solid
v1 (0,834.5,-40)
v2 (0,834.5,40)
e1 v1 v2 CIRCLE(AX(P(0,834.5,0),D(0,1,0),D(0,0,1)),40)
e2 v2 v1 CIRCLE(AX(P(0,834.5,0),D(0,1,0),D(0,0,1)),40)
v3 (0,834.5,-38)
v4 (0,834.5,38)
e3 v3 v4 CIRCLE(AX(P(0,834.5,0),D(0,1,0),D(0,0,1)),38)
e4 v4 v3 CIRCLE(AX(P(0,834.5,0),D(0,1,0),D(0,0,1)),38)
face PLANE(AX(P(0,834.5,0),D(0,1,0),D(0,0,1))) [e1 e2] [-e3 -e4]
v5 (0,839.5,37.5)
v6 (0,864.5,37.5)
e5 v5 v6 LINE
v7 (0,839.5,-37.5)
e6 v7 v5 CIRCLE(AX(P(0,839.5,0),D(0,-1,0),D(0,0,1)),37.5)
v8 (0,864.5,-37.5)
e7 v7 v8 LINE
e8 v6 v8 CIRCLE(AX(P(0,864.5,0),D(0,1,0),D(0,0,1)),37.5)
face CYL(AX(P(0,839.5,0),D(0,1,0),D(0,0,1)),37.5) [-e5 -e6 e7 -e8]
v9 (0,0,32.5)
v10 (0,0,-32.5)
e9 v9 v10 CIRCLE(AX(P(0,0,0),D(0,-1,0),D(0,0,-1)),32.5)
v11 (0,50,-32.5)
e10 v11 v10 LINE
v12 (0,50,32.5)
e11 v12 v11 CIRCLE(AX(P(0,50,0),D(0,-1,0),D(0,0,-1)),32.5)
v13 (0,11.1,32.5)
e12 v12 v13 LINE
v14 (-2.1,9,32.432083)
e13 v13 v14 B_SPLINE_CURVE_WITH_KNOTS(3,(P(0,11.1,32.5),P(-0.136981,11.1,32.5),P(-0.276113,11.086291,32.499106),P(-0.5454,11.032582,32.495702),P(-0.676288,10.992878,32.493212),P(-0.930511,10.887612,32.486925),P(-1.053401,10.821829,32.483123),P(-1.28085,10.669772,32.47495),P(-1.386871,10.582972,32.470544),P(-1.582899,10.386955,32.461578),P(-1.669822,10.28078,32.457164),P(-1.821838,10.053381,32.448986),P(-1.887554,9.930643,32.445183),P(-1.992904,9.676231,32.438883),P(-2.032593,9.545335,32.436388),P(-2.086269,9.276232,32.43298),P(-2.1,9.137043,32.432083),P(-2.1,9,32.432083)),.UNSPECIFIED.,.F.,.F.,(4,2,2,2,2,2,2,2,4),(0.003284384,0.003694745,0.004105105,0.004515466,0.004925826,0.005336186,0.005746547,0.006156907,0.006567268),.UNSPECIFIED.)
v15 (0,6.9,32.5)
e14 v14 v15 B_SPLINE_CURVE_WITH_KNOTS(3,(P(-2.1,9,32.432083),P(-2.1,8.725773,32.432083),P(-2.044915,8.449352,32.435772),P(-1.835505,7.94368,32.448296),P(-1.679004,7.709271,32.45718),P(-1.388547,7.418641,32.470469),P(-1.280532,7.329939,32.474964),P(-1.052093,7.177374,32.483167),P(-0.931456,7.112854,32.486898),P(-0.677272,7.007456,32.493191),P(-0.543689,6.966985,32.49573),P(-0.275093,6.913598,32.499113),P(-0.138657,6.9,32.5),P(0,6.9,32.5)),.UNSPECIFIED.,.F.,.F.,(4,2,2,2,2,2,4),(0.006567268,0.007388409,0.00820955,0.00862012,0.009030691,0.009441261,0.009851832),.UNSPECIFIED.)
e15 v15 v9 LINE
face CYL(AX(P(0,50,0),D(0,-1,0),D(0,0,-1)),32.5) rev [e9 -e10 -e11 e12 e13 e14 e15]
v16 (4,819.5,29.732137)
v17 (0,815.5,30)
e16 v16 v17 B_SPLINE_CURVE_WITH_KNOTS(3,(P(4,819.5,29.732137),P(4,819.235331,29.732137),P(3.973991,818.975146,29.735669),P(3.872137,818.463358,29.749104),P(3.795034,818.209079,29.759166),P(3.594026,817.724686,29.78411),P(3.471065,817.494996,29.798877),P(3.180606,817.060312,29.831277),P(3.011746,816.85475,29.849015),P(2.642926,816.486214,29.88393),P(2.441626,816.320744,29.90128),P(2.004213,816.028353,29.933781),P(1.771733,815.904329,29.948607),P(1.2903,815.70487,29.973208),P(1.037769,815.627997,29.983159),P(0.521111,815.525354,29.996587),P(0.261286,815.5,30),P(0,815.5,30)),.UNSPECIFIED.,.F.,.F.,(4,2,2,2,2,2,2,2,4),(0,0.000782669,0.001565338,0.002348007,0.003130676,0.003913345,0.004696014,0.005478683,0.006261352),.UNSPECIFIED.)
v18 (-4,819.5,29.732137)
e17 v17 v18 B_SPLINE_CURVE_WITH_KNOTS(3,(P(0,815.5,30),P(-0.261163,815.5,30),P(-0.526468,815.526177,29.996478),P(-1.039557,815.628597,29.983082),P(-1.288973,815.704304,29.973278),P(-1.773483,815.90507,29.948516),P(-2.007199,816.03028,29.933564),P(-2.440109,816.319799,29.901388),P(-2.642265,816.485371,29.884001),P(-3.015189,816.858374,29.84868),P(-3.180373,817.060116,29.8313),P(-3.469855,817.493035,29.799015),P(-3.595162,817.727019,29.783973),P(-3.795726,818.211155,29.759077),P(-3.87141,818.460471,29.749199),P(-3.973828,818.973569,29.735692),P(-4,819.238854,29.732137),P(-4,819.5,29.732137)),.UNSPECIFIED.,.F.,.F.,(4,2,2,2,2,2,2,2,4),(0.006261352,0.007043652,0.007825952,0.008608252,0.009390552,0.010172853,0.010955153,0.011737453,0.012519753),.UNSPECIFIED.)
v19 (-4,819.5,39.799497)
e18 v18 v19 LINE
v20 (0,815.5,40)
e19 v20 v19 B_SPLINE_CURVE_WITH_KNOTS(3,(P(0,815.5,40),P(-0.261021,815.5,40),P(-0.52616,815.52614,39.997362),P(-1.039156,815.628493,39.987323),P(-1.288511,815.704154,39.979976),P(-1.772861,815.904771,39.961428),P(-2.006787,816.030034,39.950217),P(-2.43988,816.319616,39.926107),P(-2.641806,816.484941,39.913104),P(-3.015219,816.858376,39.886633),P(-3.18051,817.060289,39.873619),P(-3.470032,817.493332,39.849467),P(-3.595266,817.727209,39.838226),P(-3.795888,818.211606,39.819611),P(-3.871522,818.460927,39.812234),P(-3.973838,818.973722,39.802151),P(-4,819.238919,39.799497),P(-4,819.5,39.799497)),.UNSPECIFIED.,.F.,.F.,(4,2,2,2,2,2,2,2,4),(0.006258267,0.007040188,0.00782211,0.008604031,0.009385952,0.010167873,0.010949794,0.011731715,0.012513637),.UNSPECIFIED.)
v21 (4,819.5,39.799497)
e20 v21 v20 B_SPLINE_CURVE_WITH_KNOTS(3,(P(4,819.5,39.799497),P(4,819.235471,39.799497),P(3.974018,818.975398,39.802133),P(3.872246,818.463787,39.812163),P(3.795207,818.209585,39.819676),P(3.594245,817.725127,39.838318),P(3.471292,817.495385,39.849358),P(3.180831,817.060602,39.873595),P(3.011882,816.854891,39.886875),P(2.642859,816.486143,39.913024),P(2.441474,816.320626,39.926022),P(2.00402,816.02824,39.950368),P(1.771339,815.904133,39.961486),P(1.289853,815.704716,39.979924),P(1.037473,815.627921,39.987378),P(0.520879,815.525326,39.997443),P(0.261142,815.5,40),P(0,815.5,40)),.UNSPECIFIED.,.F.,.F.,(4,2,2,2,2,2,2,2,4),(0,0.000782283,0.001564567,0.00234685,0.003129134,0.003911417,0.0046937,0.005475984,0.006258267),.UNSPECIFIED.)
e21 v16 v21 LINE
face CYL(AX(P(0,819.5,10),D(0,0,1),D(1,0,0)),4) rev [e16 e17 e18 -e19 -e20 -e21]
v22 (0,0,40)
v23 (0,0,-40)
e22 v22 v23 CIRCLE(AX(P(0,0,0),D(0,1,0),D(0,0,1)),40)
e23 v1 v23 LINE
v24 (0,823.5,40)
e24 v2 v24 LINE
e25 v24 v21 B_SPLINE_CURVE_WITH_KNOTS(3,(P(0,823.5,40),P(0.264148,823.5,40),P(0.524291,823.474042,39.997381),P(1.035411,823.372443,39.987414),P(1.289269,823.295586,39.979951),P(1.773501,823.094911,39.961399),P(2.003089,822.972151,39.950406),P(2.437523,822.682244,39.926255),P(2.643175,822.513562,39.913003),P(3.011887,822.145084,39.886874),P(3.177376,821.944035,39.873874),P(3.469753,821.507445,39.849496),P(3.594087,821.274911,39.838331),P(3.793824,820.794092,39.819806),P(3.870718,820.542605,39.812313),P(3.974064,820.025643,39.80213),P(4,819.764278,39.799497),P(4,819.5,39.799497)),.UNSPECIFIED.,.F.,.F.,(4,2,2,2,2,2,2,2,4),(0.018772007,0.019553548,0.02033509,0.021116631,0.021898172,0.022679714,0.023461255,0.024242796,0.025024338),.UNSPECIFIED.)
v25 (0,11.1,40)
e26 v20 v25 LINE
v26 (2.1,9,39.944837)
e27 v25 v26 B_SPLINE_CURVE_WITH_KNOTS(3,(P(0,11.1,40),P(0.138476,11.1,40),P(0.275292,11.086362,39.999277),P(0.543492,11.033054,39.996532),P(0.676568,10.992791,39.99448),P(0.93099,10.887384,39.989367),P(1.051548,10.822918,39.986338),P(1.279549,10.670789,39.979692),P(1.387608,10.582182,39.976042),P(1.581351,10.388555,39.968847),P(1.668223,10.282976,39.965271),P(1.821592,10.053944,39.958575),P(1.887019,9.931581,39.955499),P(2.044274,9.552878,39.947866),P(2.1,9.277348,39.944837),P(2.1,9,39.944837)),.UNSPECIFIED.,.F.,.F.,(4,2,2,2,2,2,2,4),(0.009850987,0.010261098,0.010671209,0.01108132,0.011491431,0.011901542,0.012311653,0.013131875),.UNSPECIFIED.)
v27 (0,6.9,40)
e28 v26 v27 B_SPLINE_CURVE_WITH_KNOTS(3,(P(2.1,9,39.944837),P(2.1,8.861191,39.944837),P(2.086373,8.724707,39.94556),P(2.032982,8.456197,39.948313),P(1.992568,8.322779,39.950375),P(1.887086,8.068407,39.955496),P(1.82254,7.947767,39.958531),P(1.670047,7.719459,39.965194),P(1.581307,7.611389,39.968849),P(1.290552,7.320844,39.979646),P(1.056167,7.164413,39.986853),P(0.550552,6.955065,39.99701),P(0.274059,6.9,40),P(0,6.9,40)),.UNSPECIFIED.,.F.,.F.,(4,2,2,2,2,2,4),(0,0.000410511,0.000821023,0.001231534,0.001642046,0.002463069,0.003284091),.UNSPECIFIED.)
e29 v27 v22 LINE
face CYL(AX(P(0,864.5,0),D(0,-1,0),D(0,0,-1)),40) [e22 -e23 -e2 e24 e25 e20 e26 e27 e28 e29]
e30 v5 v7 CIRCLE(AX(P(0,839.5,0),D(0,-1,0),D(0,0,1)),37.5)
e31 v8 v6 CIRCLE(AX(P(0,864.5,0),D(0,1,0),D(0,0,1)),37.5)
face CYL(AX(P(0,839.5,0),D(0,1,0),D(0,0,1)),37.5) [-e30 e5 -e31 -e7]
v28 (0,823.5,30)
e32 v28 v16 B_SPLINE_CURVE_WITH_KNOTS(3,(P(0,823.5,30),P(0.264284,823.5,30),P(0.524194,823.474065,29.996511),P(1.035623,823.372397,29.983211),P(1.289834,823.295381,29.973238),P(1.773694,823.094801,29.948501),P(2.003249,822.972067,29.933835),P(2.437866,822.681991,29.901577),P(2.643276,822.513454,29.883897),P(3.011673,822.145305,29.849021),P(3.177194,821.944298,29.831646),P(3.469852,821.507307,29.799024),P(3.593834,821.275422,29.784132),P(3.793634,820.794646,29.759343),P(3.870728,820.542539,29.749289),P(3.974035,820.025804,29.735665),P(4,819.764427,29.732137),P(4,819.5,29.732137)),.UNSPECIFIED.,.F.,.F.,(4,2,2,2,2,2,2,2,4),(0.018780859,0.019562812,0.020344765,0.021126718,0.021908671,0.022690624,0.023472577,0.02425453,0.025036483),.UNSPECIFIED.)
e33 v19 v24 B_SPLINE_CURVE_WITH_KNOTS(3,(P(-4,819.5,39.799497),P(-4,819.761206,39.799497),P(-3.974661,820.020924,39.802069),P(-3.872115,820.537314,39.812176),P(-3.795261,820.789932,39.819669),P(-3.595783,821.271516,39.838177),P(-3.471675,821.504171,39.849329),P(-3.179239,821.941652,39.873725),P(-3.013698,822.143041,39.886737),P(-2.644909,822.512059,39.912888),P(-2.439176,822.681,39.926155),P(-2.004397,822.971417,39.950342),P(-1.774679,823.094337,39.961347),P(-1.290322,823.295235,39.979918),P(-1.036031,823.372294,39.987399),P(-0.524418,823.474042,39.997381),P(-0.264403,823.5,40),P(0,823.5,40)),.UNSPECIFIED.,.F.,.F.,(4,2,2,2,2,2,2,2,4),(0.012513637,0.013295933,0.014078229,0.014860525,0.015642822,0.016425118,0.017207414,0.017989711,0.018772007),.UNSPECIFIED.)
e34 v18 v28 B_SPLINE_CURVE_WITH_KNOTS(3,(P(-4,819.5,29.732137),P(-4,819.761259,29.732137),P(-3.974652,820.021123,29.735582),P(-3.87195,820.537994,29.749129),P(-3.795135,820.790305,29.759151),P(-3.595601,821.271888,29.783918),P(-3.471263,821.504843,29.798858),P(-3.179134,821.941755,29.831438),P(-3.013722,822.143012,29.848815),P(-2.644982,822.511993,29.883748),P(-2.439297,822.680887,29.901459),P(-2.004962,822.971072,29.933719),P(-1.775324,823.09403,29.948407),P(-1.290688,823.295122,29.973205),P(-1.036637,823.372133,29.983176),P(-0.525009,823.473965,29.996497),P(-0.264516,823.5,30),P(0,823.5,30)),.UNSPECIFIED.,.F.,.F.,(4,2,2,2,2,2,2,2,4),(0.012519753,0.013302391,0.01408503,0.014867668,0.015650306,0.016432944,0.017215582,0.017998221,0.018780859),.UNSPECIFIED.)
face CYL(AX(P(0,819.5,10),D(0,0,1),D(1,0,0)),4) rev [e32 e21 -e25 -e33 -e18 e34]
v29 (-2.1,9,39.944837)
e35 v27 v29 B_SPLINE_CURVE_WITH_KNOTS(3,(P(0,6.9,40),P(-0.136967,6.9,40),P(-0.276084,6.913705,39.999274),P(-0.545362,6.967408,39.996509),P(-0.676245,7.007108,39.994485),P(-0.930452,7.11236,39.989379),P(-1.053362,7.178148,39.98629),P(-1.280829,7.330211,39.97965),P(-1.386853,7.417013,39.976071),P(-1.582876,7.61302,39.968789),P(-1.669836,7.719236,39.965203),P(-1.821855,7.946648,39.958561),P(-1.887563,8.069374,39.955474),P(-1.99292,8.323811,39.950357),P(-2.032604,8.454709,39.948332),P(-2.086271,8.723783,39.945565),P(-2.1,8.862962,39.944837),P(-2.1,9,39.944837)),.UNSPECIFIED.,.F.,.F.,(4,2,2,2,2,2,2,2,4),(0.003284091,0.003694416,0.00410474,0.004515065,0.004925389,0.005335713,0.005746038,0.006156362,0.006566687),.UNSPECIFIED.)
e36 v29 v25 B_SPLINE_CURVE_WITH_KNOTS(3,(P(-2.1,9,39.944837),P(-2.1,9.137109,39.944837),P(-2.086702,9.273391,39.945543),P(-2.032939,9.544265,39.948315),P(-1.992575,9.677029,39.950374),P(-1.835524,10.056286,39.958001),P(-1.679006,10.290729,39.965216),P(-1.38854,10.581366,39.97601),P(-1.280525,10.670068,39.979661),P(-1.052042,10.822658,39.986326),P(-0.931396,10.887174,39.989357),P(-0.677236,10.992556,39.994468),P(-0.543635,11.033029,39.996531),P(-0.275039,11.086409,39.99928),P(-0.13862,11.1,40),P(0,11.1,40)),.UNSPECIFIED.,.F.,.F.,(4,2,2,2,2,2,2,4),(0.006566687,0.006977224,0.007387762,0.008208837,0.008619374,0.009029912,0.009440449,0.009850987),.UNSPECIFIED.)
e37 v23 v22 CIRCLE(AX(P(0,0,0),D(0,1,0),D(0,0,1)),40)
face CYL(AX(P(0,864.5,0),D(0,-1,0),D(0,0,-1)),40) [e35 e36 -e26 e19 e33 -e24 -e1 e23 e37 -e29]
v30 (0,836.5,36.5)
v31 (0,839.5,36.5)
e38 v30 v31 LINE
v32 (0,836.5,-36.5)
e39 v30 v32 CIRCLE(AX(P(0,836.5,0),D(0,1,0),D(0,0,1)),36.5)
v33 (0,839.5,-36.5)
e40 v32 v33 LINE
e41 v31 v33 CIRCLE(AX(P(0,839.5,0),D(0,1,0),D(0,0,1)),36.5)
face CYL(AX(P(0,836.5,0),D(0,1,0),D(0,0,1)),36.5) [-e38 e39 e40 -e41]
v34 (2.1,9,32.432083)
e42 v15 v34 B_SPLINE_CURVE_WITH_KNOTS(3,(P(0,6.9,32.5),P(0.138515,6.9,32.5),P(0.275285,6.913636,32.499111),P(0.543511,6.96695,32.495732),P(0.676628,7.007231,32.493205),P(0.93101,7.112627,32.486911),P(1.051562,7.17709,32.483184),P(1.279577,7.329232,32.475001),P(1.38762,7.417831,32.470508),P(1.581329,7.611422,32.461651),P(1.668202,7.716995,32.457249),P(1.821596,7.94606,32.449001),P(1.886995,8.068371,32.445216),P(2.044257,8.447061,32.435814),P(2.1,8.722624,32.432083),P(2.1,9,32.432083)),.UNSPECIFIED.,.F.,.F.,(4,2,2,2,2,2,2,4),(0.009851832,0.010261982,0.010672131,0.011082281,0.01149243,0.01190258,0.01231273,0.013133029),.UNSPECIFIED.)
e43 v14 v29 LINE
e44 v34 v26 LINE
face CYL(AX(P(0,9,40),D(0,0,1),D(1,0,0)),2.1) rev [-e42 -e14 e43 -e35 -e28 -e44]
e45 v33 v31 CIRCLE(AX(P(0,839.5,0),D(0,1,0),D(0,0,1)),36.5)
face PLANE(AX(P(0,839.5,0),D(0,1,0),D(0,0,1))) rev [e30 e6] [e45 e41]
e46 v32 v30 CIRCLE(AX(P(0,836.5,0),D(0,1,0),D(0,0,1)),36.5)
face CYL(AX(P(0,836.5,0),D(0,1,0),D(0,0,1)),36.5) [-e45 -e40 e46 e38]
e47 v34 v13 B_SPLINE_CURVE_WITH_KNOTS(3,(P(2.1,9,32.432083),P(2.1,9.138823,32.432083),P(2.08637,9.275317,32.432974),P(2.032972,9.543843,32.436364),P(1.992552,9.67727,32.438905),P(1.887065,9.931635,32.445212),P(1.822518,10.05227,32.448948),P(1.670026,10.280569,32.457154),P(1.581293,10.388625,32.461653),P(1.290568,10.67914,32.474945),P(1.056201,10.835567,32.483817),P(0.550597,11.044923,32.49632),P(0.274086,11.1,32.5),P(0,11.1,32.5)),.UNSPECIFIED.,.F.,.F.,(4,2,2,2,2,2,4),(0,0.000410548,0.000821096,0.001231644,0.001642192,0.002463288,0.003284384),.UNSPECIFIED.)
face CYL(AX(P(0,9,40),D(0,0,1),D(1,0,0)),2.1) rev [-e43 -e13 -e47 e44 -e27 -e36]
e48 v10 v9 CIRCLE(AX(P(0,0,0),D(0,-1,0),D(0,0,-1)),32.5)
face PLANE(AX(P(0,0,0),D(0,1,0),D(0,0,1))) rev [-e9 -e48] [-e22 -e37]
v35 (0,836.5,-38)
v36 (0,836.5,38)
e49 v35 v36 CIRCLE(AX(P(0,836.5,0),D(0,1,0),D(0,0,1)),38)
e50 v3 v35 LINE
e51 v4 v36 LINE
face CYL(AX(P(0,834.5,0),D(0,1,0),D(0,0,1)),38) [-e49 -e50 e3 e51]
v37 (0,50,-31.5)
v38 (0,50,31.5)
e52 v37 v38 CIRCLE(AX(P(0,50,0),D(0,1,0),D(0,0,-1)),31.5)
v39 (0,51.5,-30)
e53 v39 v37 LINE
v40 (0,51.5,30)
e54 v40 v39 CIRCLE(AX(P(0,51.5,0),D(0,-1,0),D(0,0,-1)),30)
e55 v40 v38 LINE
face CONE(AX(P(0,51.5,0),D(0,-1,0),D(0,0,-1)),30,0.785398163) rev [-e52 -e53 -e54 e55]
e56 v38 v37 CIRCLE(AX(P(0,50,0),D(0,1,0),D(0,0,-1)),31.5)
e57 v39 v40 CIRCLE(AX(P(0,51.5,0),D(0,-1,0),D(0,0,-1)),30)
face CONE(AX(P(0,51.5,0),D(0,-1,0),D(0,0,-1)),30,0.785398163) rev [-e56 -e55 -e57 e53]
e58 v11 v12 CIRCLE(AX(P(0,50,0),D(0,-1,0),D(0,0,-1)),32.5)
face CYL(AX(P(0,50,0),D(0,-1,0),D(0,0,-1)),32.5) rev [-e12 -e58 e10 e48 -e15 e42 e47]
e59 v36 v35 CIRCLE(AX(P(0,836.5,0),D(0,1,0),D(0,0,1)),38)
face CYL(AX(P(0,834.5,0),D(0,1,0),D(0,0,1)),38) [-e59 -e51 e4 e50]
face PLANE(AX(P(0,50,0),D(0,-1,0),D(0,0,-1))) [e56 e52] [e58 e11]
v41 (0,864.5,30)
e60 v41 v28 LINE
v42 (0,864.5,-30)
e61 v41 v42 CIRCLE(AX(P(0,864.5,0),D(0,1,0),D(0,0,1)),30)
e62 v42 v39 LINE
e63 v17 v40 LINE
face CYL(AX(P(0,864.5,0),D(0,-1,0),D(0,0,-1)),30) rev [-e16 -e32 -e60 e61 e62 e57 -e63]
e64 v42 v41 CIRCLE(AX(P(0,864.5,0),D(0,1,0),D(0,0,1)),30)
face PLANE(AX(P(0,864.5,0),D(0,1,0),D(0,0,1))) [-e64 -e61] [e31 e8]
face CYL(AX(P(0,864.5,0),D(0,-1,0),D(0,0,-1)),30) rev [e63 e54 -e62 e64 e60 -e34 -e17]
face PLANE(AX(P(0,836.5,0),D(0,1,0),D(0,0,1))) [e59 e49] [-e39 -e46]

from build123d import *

# Parameters (mm, degrees)
SKETCH1_R             = 40
SKETCH1_R_2           = 30
BOSS_EXTRUDE1_DEPTH   = 864.5
SKETCH2_OUTSIDE_W     = 256.374
SKETCH2_OUTSIDE_H     = 256.374
SKETCH2_OUTSIDE_R     = 37.5
CUT_EXTRUDE1_DEPTH    = 25
SKETCH3_OUTSIDE_W     = 256.374
SKETCH3_OUTSIDE_H     = 256.374
SKETCH3_OUTSIDE_R     = 36.5
CUT_EXTRUDE2_DEPTH    = 3
SKETCH4_OUTSIDE_W     = 256.374
SKETCH4_OUTSIDE_H     = 256.374
SKETCH4_OUTSIDE_R     = 38
CUT_EXTRUDE3_DEPTH    = 2
SKETCH5_R             = 32.5
CUT_EXTRUDE4_DEPTH    = 50
CHAMFER2_SIZE         = 1.5
M5_TAPPED_HOLE1_D     = 4.2
M5_TAPPED_HOLE1_DEPTH = 10
M5_TAPPED_HOLE1_TIP   = 1.2618073
SKETCH8_R             = 4
CUT_EXTRUDE5_DEPTH    = 30


with BuildPart() as part:
    # Sketch1 → Boss-Extrude1 (new body)
    with BuildSketch(Plane(origin=(0, 0, 0), x_dir=(1, 0, 0), z_dir=(0, 1, 0))):
        with Locations(Location((0, 0, 0), (0, 0, 270))):
            Circle(SKETCH1_R)
        with Locations(Location((0, 0, 0), (0, 0, 270))):
            Circle(SKETCH1_R_2, mode=Mode.SUBTRACT)
    extrude(amount=BOSS_EXTRUDE1_DEPTH)

    # Sketch2 outside → Cut-Extrude1 (cut)
    with BuildSketch(Plane(origin=(0, 864.5, 0), x_dir=(1, 0, 0), z_dir=(0, 1, 0))):
        Rectangle(SKETCH2_OUTSIDE_W, SKETCH2_OUTSIDE_H)
        with Locations(Location((0, 0, 0), (0, 0, 270))):
            Circle(SKETCH2_OUTSIDE_R, mode=Mode.SUBTRACT)
    extrude(amount=-CUT_EXTRUDE1_DEPTH, mode=Mode.SUBTRACT)

    # Sketch3 outside → Cut-Extrude2 (cut)
    with BuildSketch(Plane(origin=(0, 839.5, 0), x_dir=(1, 0, 0), z_dir=(0, 1, 0))):
        Rectangle(SKETCH3_OUTSIDE_W, SKETCH3_OUTSIDE_H)
        with Locations(Location((0, 0, 0), (0, 0, 270))):
            Circle(SKETCH3_OUTSIDE_R, mode=Mode.SUBTRACT)
    extrude(amount=-CUT_EXTRUDE2_DEPTH, mode=Mode.SUBTRACT)

    # Sketch4 outside → Cut-Extrude3 (cut)
    with BuildSketch(Plane(origin=(0, 836.5, 0), x_dir=(1, 0, 0), z_dir=(0, 1, 0))):
        Rectangle(SKETCH4_OUTSIDE_W, SKETCH4_OUTSIDE_H)
        with Locations(Location((0, 0, 0), (0, 0, 270))):
            Circle(SKETCH4_OUTSIDE_R, mode=Mode.SUBTRACT)
    extrude(amount=-CUT_EXTRUDE3_DEPTH, mode=Mode.SUBTRACT)

    # Sketch5 → Cut-Extrude4 (cut)
    with BuildSketch(Plane.XZ):
        with Locations(Location((0, 0, 0), (0, 0, 270))):
            Circle(SKETCH5_R)
    extrude(amount=-CUT_EXTRUDE4_DEPTH, mode=Mode.SUBTRACT)

    # Chamfer2
    chamfer2_edges = [part.edges().sort_by_distance(p)[0] for p in [
        (0, 50, -30),
    ]]
    chamfer(chamfer2_edges, length=CHAMFER2_SIZE)

    # M5 Tapped Hole1
    with Locations(Plane.XY.offset(40)):
        with Locations((0, 9)):
            Hole(M5_TAPPED_HOLE1_D / 2, depth=M5_TAPPED_HOLE1_DEPTH)
            with Locations((0, 0, -(M5_TAPPED_HOLE1_DEPTH + M5_TAPPED_HOLE1_TIP / 2))):  # 118° drill point
                Cone(0, M5_TAPPED_HOLE1_D / 2, M5_TAPPED_HOLE1_TIP, mode=Mode.SUBTRACT)

    # Sketch8 → Cut-Extrude5 (cut)
    with BuildSketch(Plane.XY.offset(40)):
        with Locations((0, 819.5)):
            Circle(SKETCH8_R)
    extrude(amount=-CUT_EXTRUDE5_DEPTH, mode=Mode.SUBTRACT)


solid = part.part
